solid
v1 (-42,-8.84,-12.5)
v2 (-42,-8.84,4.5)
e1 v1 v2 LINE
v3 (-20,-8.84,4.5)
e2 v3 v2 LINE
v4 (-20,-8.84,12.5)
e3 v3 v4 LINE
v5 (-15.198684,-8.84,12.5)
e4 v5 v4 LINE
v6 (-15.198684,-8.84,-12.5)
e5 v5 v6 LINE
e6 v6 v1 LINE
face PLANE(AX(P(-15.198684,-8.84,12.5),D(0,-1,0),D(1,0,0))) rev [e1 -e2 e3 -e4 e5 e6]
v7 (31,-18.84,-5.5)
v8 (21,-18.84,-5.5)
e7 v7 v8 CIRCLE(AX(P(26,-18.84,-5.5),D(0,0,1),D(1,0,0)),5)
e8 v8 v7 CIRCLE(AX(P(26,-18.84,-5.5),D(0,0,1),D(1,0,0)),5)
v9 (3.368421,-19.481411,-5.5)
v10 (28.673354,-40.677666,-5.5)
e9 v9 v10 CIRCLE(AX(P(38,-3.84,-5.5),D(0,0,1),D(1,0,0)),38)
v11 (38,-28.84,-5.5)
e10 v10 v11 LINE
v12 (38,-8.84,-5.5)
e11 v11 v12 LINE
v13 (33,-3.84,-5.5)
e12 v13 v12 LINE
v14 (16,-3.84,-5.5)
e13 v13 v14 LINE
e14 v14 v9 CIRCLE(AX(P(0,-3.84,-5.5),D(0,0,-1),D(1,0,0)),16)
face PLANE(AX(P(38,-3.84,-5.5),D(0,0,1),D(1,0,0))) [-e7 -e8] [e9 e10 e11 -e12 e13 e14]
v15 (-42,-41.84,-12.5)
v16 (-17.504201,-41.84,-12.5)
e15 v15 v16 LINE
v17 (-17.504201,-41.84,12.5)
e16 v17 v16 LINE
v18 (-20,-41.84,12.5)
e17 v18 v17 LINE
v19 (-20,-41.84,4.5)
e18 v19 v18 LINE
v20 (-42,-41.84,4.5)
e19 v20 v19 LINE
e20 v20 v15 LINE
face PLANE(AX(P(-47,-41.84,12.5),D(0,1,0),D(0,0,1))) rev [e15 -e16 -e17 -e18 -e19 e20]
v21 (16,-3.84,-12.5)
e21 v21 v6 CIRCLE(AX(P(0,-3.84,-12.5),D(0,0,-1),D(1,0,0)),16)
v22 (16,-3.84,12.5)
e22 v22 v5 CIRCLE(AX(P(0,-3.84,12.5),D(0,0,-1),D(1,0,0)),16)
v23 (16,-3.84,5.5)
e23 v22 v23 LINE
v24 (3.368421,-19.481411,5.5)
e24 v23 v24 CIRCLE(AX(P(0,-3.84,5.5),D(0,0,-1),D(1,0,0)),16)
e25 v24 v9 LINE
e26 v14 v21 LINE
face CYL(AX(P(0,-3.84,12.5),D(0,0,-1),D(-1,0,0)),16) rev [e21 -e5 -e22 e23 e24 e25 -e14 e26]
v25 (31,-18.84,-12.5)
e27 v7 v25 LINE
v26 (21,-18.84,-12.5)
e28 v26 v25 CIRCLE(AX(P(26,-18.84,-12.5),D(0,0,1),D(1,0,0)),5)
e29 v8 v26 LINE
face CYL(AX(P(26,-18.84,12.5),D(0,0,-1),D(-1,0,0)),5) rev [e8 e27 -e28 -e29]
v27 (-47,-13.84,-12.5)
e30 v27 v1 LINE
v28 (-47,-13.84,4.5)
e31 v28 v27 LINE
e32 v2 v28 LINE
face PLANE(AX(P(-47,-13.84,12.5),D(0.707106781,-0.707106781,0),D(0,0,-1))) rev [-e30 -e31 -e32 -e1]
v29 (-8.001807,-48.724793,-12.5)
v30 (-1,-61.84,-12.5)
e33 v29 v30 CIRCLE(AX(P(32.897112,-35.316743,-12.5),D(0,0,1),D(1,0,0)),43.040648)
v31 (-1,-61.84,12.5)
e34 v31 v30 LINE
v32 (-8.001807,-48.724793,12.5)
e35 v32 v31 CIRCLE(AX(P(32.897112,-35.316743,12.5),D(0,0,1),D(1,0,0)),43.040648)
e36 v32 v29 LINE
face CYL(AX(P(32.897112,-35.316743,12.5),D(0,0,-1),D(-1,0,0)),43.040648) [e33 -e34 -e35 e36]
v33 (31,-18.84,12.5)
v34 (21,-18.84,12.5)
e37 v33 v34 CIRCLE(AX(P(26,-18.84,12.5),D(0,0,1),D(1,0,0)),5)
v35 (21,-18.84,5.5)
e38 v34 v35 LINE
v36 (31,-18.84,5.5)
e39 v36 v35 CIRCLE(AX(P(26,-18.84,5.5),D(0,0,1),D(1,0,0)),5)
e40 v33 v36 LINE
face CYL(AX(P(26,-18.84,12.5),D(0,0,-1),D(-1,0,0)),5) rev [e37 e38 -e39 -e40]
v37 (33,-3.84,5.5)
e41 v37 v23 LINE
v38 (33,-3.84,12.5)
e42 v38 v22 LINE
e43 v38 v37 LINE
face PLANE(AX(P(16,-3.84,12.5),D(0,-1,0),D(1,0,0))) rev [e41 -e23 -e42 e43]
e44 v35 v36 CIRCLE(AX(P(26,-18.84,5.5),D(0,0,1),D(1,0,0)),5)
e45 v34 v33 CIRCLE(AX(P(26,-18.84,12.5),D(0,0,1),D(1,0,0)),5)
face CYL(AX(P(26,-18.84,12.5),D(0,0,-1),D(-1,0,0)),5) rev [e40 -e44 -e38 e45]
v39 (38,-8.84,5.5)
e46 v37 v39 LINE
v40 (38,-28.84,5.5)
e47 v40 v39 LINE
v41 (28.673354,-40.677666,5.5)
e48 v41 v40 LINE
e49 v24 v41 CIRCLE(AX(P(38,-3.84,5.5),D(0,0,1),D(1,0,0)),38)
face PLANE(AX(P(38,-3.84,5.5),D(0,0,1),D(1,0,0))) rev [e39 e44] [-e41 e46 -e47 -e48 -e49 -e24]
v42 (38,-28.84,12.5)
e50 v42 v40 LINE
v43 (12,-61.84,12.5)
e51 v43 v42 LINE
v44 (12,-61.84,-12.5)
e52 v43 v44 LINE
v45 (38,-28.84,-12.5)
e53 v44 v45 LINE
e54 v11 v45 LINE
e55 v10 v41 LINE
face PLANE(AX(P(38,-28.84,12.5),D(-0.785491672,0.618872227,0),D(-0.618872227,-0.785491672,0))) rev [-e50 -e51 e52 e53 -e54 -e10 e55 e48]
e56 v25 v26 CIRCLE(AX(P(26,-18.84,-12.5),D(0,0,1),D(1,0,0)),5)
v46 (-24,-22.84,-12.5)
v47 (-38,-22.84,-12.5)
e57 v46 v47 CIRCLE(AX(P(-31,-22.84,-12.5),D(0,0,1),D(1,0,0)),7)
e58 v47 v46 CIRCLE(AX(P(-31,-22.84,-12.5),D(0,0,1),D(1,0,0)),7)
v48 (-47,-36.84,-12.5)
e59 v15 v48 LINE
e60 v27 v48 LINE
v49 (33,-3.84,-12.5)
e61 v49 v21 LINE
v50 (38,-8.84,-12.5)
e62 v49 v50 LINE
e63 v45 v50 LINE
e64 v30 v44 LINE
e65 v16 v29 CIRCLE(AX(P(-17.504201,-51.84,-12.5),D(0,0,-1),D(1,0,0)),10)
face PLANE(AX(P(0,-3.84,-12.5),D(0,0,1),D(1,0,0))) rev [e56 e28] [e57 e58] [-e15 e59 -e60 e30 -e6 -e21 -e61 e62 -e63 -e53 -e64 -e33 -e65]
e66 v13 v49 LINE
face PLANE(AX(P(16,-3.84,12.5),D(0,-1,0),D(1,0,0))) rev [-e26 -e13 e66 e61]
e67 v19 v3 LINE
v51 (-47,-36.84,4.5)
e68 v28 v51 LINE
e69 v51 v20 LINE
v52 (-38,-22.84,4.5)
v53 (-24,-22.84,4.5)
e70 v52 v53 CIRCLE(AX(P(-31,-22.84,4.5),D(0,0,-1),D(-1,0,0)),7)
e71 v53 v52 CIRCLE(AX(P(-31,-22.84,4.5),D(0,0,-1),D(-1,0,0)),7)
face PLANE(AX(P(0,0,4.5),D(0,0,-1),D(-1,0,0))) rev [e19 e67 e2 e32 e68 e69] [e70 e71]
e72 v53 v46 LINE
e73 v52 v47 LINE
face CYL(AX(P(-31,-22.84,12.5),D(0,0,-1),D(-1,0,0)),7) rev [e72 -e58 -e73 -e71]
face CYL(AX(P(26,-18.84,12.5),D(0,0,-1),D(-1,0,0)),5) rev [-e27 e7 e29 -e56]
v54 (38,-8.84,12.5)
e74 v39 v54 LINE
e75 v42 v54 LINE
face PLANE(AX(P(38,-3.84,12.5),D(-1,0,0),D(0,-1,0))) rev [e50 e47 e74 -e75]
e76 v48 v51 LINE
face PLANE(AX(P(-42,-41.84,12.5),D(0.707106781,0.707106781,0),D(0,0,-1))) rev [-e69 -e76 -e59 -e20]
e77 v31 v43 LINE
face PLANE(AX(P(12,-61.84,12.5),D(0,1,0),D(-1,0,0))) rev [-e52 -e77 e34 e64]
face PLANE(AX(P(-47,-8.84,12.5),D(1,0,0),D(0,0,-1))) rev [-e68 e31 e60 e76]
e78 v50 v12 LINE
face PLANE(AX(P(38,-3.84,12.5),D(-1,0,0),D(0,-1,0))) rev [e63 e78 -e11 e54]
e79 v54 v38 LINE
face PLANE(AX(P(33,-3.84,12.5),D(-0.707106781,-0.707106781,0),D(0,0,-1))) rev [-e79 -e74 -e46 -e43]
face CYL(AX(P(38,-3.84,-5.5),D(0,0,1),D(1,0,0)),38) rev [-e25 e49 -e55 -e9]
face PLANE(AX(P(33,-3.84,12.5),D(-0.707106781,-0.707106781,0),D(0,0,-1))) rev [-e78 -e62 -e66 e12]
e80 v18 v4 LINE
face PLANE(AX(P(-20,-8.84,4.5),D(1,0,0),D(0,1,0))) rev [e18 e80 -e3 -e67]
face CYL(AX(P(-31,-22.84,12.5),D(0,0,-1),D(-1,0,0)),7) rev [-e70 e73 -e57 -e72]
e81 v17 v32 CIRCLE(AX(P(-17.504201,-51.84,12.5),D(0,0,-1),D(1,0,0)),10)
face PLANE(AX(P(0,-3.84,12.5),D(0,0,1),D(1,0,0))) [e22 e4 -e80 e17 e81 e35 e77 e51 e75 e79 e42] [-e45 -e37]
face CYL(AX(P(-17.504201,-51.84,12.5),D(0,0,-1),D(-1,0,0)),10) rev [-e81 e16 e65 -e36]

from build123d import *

# Parameters (mm, degrees)
BRACKET_PROFILE_SKETCH_R   = 7
BRACKET_PROFILE_SKETCH_R_2 = 5
BRACKET_BODY_25MM_DEPTH    = 12.5
EDGE_CHAMFER_5MM_SIZE      = 5
SLOT_SKETCH_W              = 27
SLOT_SKETCH_H              = 33
SLOT_CUT_8MM_DEPTH         = 8
CROSS_HOLE_SKETCH_R        = 38
CROSS_HOLE_CUT_DEPTH       = 5.5


with BuildPart() as part:
    # Bracket Profile Sketch → Bracket Body 25mm (new, symmetric)
    with BuildSketch(Plane.XY):
        with BuildLine():
            Line((16, -3.84), (38, -3.84))
            Line((38, -3.84), (38, -28.84))
            Line((38, -28.84), (12, -61.84))
            Line((12, -61.84), (-1, -61.84))
            ThreePointArc((-1, -61.84), (-5.071476538, -55.587008251), (-8.001806768, -48.724793466))
            ThreePointArc((-8.001806768, -48.724793466), (-11.637006424, -43.74209702), (-17.504200585, -41.84))
            Line((-17.504200585, -41.84), (-47, -41.84))
            Line((-47, -41.84), (-47, -8.84))
            Line((-47, -8.84), (-15.198684154, -8.84))
            ThreePointArc((-15.198684154, -8.84), (2.531901809, -19.638400971), (16, -3.84))
        make_face()
        with Locations((-31, -22.84)):
            Circle(BRACKET_PROFILE_SKETCH_R, mode=Mode.SUBTRACT)
        with Locations((26, -18.84)):
            Circle(BRACKET_PROFILE_SKETCH_R_2, mode=Mode.SUBTRACT)
    extrude(amount=BRACKET_BODY_25MM_DEPTH, both=True)

    # Edge Chamfer 5mm
    edge_chamfer_5mm_edges = [part.edges().sort_by_distance(p)[0] for p in [
        (38, -3.84, 0),
        (-47, -41.84, 0),
        (-47, -8.84, 0),
    ]]
    chamfer(edge_chamfer_5mm_edges, length=EDGE_CHAMFER_5MM_SIZE)

    # Slot Sketch → Slot Cut 8mm (cut)
    with BuildSketch(Plane.XY.offset(12.5)):
        with Locations((-33.5, -25.34)):
            Rectangle(SLOT_SKETCH_W, SLOT_SKETCH_H)
    extrude(amount=-SLOT_CUT_8MM_DEPTH, mode=Mode.SUBTRACT)

    # Cross Hole Sketch → Cross Hole Cut (cut, symmetric)
    with BuildSketch(Plane.XY):
        with Locations((38, -3.84)):
            Circle(CROSS_HOLE_SKETCH_R)
    extrude(amount=CROSS_HOLE_CUT_DEPTH, both=True, mode=Mode.SUBTRACT)


solid = part.part
